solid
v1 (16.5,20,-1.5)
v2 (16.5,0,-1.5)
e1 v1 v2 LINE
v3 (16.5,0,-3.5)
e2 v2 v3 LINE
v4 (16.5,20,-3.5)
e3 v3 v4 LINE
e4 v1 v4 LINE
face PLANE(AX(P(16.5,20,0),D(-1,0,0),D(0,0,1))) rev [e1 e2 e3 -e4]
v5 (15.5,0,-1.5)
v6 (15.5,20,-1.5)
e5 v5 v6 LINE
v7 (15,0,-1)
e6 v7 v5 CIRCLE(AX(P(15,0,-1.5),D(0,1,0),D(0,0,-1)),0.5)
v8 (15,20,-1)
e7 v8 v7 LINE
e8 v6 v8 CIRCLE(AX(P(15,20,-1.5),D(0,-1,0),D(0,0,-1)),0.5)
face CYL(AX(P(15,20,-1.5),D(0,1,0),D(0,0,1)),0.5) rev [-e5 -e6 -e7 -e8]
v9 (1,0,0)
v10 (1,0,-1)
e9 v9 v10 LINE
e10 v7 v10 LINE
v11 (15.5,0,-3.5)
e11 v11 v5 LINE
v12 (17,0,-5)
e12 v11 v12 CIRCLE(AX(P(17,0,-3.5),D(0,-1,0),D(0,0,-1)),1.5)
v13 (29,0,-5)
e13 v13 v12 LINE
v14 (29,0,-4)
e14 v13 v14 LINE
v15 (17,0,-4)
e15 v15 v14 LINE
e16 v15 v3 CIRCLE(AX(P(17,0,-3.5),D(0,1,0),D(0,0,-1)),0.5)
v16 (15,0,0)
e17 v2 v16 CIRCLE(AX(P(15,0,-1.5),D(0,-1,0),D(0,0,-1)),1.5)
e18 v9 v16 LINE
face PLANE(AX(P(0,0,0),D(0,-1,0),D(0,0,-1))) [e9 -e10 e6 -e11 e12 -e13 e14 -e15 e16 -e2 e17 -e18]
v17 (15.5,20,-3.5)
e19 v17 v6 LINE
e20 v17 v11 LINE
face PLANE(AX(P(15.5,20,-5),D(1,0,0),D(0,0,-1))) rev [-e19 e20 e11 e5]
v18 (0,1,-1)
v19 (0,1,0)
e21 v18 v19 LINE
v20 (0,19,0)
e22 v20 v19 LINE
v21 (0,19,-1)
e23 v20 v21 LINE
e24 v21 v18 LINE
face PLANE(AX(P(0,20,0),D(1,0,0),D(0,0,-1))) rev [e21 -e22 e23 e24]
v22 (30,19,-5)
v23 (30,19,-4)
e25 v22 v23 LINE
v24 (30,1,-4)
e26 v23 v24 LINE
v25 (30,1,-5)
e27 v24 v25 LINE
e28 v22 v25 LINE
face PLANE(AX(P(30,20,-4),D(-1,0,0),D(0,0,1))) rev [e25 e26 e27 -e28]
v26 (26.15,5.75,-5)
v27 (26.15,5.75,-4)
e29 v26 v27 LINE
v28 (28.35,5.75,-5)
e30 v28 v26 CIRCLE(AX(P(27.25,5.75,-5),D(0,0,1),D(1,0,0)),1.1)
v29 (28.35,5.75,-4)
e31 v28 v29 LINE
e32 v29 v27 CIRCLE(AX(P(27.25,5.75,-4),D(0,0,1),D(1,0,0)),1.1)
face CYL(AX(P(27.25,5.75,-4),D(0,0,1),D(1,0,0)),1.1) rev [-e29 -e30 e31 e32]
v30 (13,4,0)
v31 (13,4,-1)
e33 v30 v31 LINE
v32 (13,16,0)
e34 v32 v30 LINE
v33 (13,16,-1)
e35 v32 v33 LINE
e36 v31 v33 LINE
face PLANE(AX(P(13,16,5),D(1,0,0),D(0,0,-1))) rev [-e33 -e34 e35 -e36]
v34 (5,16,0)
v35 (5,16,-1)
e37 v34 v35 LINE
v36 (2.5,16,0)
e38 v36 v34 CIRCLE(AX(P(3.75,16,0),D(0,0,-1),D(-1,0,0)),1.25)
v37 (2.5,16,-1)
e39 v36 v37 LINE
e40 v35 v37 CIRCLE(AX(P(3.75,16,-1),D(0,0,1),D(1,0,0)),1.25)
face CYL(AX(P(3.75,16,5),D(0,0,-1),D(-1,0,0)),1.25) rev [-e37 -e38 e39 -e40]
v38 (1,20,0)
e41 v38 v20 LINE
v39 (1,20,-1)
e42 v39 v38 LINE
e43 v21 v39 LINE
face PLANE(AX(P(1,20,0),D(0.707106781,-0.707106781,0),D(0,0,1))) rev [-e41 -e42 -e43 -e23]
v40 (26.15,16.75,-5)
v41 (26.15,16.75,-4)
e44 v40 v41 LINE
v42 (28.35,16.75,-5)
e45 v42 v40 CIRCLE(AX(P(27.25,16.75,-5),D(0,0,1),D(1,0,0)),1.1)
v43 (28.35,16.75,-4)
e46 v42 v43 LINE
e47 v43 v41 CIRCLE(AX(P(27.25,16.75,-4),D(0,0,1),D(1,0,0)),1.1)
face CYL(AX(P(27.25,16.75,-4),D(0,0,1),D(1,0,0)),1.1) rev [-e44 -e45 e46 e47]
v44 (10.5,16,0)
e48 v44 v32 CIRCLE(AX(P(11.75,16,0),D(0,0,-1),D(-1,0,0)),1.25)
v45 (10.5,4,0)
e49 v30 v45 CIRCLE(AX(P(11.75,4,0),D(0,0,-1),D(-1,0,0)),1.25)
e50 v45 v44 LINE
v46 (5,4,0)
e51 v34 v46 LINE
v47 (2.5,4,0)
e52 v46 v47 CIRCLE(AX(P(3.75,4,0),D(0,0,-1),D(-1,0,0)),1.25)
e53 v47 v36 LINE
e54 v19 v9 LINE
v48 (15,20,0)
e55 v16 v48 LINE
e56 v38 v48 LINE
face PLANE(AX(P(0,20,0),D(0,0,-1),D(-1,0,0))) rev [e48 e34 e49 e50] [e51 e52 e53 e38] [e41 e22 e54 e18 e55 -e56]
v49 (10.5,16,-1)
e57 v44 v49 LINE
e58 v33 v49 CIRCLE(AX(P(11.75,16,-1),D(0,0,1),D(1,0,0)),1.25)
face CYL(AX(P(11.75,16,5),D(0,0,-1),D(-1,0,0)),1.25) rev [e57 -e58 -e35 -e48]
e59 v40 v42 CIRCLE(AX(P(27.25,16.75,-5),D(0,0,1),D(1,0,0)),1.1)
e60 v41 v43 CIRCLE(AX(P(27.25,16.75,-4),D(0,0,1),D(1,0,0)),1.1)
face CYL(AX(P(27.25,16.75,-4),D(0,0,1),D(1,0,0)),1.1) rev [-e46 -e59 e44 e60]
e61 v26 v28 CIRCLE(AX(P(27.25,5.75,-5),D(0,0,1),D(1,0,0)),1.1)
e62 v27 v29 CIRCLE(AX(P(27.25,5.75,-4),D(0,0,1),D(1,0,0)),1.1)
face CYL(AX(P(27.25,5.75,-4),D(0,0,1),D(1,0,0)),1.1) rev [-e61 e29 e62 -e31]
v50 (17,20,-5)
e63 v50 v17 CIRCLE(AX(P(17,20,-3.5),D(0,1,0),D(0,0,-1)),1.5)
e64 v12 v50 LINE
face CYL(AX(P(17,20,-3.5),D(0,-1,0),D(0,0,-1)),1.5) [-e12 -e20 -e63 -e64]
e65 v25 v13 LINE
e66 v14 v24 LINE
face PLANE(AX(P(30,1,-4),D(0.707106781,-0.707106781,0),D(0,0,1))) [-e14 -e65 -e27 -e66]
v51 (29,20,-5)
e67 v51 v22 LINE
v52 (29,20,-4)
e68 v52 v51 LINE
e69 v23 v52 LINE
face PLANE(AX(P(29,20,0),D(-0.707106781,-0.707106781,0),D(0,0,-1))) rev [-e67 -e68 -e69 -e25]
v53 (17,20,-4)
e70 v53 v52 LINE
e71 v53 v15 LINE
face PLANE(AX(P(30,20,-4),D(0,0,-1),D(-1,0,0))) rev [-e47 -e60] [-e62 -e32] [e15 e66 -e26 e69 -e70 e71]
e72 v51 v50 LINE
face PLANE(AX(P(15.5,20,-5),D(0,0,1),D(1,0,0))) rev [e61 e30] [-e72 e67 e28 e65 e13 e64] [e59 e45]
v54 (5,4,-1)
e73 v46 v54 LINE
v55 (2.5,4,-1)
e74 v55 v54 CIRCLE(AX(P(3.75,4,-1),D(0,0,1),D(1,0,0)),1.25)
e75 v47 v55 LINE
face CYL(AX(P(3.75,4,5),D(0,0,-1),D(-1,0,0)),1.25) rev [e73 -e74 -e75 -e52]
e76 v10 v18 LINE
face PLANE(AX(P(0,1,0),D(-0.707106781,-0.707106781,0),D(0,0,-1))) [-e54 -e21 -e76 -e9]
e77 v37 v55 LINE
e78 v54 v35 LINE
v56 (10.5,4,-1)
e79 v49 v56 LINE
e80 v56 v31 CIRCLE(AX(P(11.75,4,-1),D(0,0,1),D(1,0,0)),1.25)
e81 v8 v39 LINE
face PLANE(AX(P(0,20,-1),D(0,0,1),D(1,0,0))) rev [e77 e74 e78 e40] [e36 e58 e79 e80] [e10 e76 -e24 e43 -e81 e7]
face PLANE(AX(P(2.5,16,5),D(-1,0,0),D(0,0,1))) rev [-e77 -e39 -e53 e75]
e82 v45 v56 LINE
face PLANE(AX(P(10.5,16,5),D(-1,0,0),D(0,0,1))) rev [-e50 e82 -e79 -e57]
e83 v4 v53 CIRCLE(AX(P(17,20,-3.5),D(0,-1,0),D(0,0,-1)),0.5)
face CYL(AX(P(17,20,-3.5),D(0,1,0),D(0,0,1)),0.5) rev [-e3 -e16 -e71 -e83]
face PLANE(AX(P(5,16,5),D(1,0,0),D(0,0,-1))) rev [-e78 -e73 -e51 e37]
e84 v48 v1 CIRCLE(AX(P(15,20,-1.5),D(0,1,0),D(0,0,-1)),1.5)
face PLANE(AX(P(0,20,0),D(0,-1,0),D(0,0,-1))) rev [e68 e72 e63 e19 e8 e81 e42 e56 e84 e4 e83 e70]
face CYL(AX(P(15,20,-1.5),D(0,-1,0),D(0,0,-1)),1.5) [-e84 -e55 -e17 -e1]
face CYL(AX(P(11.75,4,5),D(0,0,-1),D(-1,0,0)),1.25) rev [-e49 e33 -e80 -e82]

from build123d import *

# Parameters (mm, degrees)
BOSS_EXTRUDE1_DEPTH            = 20
CUT_EXTRUDE1_DEPTH             = 10
CHAMFER1_SIZE                  = 1
FILLET1_R                      = 1.5
FILLET2_R                      = 0.5
F_2_2_2_2_DIAMETER_HOLE1_D     = 2.2
F_2_2_2_2_DIAMETER_HOLE1_DEPTH = 5
F_2_2_2_2_DIAMETER_HOLE1_TIP   = 0.660946681


with BuildPart() as part:
    # Sketch1 → Boss-Extrude1 (new body)
    with BuildSketch(Plane(origin=(0, 0, 0), x_dir=(1, 0, 0), z_dir=(0, 1, 0))):
        Polygon((0, 0), (16.5, 0), (16.5, 4), (30, 4), (30, 5), (15.5, 5), (15.5, 1), (0, 1), align=None)
    extrude(amount=BOSS_EXTRUDE1_DEPTH)

    # Sketch2 → Cut-Extrude1 (cut)
    with BuildSketch(Plane(origin=(0, 0, -5), x_dir=(-1, 0, 0), z_dir=(0, 0, -1))):
        with BuildLine():
            Line((-10.5, 16), (-10.5, 4))
            ThreePointArc((-10.5, 4), (-11.75, 2.75), (-13, 4))
            Line((-13, 4), (-13, 16))
            ThreePointArc((-13, 16), (-11.75, 17.25), (-10.5, 16))
        make_face()
        with BuildLine():
            Line((-5, 16), (-5, 4))
            ThreePointArc((-5, 4), (-3.75, 2.75), (-2.5, 4))
            Line((-2.5, 4), (-2.5, 16))
            ThreePointArc((-2.5, 16), (-3.75, 17.25), (-5, 16))
        make_face()
    extrude(amount=-CUT_EXTRUDE1_DEPTH, mode=Mode.SUBTRACT)

    # Chamfer1
    chamfer1_edges = [part.edges().sort_by_distance(p)[0] for p in [
        (0, 0, -0.5),
        (30, 20, -4.5),
        (0, 20, -0.5),
        (30, 0, -4.5),
    ]]
    chamfer(chamfer1_edges, length=CHAMFER1_SIZE)

    # Fillet1
    fillet1_edges = [part.edges().sort_by_distance(p)[0] for p in [
        (15.5, 10, -5),
        (16.5, 10, 0),
    ]]
    fillet(fillet1_edges, radius=FILLET1_R)

    # Fillet2
    fillet2_edges = [part.edges().sort_by_distance(p)[0] for p in [
        (15.5, 10, -1),
        (16.5, 10, -4),
    ]]
    fillet(fillet2_edges, radius=FILLET2_R)

    # Ø2.2 (2.2) Diameter Hole1
    with Locations(Plane.XY.offset(-4)):
        with Locations((27.25, 16.75), (27.25, 5.75)):
            Hole(F_2_2_2_2_DIAMETER_HOLE1_D / 2, depth=F_2_2_2_2_DIAMETER_HOLE1_DEPTH)
            with Locations((0, 0, -(F_2_2_2_2_DIAMETER_HOLE1_DEPTH + F_2_2_2_2_DIAMETER_HOLE1_TIP / 2))):  # 118° drill point
                Cone(0, F_2_2_2_2_DIAMETER_HOLE1_D / 2, F_2_2_2_2_DIAMETER_HOLE1_TIP, mode=Mode.SUBTRACT)


solid = part.part
